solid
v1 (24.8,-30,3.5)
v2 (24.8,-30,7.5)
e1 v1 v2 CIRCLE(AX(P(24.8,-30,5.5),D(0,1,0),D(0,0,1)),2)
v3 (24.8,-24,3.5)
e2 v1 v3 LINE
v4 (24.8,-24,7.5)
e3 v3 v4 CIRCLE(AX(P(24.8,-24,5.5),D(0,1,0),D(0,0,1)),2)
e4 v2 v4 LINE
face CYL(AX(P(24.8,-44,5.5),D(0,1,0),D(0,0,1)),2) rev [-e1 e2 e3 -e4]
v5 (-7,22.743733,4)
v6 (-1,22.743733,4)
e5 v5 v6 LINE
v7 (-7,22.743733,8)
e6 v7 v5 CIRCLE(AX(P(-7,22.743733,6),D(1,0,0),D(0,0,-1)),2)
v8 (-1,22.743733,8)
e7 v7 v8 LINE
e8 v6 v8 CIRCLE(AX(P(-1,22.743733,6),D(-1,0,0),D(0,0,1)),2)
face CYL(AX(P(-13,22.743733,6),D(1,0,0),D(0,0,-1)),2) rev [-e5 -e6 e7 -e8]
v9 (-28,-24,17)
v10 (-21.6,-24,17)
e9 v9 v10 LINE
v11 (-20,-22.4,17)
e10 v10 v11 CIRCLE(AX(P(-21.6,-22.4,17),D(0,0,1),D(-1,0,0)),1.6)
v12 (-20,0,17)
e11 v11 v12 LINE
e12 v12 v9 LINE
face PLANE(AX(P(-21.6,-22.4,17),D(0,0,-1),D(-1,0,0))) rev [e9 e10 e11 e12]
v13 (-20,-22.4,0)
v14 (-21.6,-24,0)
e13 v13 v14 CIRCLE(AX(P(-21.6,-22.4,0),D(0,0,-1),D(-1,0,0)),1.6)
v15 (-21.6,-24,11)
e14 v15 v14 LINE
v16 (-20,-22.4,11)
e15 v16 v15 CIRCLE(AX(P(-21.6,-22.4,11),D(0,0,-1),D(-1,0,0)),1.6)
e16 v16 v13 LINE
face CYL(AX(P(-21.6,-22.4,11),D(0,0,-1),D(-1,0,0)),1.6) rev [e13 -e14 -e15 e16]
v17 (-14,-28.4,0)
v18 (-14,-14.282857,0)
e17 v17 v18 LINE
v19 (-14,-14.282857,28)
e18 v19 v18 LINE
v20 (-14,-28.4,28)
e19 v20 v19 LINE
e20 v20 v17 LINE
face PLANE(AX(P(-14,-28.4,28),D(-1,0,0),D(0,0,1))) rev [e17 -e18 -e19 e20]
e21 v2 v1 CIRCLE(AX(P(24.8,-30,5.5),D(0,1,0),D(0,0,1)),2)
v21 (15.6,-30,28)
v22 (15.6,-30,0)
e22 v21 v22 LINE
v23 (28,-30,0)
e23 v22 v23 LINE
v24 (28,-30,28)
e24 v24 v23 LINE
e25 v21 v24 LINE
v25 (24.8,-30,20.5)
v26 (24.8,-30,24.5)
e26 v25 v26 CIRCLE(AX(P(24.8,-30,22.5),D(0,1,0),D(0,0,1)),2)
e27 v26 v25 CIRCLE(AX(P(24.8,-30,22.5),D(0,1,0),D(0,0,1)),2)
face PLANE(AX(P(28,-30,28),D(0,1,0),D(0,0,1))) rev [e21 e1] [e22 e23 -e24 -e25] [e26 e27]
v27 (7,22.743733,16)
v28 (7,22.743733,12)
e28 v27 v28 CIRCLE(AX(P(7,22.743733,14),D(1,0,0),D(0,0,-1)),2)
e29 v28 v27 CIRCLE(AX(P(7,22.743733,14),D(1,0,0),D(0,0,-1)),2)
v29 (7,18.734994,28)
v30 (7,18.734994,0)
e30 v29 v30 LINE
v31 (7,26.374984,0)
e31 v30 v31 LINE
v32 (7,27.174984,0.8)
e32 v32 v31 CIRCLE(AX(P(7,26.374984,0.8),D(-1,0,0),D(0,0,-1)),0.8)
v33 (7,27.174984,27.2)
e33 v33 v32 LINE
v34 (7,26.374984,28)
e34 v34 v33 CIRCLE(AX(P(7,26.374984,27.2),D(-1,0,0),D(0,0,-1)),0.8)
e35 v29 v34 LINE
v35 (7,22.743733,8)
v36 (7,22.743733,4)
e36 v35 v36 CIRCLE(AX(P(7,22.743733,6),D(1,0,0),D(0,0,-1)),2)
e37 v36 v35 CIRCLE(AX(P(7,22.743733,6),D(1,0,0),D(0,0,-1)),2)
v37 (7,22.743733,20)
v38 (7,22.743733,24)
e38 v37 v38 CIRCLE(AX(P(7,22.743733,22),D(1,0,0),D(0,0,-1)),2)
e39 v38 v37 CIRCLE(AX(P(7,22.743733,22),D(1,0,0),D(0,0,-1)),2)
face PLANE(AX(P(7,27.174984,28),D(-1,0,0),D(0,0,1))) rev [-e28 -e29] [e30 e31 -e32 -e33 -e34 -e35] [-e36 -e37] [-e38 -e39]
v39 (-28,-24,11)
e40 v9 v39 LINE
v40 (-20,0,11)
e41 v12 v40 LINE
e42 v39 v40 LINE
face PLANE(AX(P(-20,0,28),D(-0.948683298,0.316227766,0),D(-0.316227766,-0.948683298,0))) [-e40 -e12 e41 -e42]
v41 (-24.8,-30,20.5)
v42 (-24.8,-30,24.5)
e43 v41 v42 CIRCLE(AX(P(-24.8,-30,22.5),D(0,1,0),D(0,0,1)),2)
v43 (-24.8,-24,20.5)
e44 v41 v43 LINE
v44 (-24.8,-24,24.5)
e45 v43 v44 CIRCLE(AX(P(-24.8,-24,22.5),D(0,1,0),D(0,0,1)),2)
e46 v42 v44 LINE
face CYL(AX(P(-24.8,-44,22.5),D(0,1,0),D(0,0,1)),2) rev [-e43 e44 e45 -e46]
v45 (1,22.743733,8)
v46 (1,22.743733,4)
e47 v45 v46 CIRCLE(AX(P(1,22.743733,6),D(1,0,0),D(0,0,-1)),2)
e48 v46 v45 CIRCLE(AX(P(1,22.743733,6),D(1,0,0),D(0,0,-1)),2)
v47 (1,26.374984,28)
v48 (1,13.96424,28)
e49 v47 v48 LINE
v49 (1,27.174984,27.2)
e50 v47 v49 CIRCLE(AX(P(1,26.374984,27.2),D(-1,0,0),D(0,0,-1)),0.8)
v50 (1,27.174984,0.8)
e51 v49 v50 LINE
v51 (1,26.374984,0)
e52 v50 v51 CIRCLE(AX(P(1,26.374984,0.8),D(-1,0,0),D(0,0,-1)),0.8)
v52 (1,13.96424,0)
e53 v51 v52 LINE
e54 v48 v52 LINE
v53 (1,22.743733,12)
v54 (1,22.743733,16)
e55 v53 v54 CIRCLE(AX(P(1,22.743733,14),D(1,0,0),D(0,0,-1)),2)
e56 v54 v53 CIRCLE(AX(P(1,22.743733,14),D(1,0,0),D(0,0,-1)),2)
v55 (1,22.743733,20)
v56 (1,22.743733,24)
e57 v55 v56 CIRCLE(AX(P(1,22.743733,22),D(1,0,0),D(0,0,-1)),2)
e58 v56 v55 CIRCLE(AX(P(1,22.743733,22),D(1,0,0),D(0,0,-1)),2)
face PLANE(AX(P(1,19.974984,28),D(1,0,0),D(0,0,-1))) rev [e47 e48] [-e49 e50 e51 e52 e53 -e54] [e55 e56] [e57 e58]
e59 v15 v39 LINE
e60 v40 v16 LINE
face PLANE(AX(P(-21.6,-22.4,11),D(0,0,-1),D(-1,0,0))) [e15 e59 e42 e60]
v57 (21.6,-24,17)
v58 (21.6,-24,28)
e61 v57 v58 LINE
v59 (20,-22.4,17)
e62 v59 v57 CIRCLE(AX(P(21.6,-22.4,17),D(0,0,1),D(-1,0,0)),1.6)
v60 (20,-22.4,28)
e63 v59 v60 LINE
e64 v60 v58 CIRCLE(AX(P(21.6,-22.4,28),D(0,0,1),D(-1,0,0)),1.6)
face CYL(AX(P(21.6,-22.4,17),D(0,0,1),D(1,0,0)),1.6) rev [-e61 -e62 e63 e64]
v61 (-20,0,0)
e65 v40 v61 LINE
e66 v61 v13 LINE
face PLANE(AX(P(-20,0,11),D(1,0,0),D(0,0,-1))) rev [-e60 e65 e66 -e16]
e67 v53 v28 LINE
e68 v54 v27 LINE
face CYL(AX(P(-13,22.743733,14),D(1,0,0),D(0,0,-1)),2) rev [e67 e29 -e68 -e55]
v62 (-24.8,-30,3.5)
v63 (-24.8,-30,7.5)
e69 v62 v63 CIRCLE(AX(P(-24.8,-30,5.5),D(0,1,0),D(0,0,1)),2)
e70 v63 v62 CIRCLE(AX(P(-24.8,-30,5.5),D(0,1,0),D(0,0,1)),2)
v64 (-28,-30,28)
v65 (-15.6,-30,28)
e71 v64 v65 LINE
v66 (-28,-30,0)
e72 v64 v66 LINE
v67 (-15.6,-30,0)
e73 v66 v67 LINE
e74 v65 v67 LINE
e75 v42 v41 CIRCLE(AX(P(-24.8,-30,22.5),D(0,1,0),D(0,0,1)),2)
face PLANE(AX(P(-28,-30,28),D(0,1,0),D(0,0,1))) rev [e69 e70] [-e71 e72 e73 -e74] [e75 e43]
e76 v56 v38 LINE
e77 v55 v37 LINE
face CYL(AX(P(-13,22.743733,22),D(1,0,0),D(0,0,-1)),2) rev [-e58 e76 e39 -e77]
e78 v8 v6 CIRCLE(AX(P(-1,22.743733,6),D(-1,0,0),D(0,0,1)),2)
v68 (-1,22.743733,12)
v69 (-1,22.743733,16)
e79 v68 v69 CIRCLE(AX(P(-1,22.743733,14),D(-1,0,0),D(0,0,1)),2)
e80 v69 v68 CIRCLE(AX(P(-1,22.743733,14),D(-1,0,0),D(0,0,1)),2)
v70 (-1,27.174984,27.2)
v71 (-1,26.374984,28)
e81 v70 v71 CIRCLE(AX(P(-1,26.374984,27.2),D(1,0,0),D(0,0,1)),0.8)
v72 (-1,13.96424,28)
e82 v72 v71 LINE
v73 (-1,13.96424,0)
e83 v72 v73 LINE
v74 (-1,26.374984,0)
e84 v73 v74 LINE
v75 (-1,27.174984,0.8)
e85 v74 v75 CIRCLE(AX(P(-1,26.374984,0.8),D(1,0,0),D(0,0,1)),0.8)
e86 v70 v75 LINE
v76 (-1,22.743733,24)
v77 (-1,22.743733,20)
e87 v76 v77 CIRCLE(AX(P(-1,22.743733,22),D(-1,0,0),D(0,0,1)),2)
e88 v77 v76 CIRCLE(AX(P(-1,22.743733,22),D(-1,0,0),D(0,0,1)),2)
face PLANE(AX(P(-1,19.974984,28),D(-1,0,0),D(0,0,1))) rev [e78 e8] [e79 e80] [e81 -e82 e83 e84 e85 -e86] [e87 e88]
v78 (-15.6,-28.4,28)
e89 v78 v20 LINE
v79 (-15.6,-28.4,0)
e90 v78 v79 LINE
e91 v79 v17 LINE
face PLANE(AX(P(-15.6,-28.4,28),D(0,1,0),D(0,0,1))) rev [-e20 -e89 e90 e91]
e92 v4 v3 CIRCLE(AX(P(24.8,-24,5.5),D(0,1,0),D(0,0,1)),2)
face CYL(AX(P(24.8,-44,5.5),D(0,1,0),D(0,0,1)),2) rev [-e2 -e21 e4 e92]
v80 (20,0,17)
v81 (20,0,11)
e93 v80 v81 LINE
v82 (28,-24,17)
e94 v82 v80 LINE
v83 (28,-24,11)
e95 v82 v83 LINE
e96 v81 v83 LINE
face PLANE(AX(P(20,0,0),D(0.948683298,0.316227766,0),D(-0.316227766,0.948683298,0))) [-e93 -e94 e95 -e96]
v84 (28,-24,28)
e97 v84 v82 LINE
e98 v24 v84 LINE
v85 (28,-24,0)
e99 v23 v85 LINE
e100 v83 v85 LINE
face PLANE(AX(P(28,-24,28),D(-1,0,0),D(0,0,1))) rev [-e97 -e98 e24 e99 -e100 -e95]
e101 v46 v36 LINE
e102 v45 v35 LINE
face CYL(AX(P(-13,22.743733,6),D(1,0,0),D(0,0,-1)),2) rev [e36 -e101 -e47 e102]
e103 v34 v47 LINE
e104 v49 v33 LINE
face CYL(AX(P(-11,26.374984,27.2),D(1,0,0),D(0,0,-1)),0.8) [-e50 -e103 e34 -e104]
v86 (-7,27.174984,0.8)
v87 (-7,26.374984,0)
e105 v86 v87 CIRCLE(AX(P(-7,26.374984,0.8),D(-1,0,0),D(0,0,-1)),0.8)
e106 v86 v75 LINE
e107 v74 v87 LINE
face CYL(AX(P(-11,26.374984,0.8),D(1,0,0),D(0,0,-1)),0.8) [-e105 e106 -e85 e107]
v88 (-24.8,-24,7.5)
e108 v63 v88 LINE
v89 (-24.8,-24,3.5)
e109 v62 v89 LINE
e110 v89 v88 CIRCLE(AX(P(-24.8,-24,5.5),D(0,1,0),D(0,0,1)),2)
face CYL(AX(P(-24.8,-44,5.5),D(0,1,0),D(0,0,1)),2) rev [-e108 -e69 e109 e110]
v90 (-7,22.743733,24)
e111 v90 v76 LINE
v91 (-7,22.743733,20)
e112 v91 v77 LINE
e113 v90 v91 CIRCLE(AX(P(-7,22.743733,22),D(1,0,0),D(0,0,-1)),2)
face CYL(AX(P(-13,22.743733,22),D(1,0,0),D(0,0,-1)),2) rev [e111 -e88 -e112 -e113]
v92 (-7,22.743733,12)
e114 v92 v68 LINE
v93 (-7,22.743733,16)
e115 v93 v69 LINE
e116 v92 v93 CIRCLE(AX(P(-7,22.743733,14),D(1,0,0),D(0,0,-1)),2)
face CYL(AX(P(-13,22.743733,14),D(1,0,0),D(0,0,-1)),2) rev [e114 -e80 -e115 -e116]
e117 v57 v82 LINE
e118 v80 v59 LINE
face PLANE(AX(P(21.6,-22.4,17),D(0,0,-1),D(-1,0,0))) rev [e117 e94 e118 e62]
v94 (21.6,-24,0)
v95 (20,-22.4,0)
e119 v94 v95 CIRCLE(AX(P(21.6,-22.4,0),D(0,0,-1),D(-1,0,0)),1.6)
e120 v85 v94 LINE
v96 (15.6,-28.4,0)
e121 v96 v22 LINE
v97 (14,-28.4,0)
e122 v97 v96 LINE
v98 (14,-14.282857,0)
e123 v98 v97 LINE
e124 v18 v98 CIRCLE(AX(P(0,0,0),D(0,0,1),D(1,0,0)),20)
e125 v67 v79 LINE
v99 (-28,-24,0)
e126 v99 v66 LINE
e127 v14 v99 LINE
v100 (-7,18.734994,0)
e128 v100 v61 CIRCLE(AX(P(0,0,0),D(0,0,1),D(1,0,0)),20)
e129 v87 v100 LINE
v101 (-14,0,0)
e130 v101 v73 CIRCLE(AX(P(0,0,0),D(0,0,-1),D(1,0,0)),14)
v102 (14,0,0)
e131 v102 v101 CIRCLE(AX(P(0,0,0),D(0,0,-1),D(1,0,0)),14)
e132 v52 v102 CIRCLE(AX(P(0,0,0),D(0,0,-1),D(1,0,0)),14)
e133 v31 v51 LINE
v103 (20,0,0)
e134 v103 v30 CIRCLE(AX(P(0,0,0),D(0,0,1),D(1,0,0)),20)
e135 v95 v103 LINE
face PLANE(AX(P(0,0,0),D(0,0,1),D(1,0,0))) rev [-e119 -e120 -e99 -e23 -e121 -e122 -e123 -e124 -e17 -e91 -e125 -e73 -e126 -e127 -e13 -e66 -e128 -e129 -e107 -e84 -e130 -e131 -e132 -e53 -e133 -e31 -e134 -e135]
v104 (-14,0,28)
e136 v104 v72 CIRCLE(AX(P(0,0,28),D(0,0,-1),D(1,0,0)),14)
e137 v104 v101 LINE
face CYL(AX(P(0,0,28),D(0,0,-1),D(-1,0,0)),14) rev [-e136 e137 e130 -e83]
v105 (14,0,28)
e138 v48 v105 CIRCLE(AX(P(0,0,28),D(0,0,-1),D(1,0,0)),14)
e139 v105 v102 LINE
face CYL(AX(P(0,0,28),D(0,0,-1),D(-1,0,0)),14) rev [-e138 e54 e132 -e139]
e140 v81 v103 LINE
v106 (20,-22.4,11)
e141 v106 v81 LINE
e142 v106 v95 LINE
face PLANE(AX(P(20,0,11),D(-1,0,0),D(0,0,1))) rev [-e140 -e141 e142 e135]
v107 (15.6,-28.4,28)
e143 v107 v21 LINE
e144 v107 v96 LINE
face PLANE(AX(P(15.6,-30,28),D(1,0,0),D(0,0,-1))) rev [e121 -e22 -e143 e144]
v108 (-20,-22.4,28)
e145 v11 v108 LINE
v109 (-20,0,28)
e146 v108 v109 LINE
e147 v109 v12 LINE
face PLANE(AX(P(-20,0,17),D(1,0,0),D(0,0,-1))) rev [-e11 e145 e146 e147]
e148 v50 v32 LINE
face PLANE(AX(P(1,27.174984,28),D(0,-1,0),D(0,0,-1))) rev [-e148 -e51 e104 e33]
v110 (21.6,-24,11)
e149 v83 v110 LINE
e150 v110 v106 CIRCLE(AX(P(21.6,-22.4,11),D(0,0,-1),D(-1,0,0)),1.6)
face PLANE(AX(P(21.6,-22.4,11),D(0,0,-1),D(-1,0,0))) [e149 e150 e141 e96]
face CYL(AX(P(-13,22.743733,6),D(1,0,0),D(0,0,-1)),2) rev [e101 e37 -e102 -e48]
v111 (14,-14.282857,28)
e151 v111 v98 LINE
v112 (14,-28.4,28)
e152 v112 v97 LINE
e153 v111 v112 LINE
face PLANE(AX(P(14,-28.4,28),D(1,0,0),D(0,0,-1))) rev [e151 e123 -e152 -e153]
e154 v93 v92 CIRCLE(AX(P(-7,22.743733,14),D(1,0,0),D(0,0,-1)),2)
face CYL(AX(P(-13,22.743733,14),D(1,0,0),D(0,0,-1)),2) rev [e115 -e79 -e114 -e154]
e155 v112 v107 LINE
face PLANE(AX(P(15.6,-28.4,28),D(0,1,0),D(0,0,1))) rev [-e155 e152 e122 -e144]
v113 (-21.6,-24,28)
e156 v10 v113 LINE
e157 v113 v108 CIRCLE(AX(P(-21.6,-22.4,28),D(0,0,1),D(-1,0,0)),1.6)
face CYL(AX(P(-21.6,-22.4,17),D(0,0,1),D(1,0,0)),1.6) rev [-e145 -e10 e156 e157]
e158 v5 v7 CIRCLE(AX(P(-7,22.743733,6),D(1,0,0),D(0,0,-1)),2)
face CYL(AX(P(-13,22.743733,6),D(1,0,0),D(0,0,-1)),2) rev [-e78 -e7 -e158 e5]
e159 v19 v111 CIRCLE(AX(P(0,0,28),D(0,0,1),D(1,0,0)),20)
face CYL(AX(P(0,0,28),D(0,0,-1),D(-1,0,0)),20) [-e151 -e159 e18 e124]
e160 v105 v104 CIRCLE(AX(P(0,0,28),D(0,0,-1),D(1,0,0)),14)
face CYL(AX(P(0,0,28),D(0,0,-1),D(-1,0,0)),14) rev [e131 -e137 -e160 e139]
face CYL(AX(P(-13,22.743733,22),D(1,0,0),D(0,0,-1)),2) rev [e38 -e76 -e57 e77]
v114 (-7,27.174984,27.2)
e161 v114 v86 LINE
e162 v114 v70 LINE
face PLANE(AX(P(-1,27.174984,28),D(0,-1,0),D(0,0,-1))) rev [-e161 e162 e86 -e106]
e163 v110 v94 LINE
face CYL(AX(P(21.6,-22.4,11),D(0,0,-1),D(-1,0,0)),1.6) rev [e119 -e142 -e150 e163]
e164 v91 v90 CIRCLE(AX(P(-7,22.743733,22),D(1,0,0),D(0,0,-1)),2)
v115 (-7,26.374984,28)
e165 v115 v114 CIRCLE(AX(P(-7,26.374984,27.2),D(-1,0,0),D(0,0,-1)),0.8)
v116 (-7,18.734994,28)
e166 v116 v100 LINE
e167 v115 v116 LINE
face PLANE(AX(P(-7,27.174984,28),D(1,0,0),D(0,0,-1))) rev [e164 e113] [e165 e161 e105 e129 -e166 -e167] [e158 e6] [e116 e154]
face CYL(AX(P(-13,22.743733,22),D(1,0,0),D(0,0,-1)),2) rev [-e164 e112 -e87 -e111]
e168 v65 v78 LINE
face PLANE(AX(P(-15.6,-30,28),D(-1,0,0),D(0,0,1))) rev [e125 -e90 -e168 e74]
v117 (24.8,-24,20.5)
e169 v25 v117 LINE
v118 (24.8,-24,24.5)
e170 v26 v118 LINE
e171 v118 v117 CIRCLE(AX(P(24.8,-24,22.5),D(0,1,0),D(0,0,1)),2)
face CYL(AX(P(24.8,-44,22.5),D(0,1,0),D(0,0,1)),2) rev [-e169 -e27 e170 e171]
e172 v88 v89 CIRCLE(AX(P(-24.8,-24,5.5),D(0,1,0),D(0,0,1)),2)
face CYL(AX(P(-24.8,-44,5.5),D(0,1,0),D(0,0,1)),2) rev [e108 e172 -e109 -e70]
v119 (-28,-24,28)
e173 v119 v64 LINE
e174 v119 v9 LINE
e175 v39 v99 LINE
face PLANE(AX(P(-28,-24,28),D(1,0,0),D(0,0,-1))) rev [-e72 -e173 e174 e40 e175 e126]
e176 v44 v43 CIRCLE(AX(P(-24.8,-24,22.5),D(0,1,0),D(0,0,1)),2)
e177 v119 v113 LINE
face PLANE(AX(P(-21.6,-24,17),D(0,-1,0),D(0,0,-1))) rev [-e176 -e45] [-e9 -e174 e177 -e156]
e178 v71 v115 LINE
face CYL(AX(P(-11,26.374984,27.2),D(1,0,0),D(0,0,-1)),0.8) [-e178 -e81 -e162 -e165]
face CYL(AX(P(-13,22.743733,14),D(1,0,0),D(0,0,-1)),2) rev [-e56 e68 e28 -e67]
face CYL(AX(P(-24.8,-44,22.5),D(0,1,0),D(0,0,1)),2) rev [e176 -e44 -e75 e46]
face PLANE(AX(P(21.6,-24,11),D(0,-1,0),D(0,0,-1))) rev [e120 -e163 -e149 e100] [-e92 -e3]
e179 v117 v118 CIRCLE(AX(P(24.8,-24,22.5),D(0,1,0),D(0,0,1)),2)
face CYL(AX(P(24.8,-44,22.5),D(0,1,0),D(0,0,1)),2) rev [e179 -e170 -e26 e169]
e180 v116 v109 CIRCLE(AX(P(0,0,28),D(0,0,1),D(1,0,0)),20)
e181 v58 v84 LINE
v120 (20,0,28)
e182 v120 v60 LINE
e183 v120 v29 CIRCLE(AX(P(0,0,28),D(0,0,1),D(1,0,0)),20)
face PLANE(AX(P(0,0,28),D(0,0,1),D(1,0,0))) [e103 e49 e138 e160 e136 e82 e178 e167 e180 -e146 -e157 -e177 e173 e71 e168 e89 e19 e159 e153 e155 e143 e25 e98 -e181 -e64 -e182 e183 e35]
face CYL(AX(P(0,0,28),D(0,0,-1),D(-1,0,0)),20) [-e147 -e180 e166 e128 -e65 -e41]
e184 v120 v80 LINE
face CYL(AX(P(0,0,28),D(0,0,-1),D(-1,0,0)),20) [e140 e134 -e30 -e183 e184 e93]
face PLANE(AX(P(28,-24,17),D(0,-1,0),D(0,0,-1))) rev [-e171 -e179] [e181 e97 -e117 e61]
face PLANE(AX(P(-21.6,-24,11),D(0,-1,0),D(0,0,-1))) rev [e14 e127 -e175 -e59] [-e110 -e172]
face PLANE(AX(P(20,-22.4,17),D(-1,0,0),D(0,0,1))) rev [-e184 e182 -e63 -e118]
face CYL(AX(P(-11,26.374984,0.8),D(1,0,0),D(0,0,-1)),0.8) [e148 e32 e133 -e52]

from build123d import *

# Parameters (mm, degrees)
CLAMP_BODY_DEPTH             = 28
SIDE_RECESS_A_DEPTH          = 18
SIDE_RECESS_B_DEPTH          = 18
LOWER_START                  = -28
LOWER_SIDE_BOSS_DEPTH        = 28
LOWER_BOSS_RELIEF_A_DEPTH    = 11
LOWER_START_2                = -11
LOWER_BOSS_RELIEF_B_DEPTH    = 11
UPPER_SIDE_BOSS_DEPTH        = 28
UPPER_BOSS_RELIEF_A_DEPTH    = 11
UPPER_START                  = -11
UPPER_BOSS_RELIEF_B_DEPTH    = 11
CLAMP_SCREW_HOLES_SKETCH_R   = 2
CLAMP_SCREW_HOLES_3X_DEPTH   = 20
FOOT_MOUNTING_HOLES_SKETCH_R = 2
FOOT_MOUNTING_HOLES_DEPTH    = 20


with BuildPart() as part:
    # Clamp Body Profile → Clamp Body (new body)
    with BuildSketch(Plane.XY):
        with BuildLine():
            Line((-20, 0), (-20, -22.4))
            ThreePointArc((-20, -22.4), (-20.46862915, -23.53137085), (-21.6, -24))
            Line((-21.6, -24), (-28, -24))
            Line((-28, -24), (-28, -30))
            Line((-28, -30), (-15.6, -30))
            Line((-15.6, -30), (-15.6, -28.4))
            Line((-15.6, -28.4), (-14, -28.4))
            Line((-14, -28.4), (-14, -14.282856857))
            ThreePointArc((-14, -14.282856857), (0, -20), (14, -14.282856857))
            Line((14, -14.282856857), (14, -28.4))
            Line((14, -28.4), (15.6, -28.4))
            Line((15.6, -28.4), (15.6, -30))
            Line((15.6, -30), (28, -30))
            Line((28, -30), (28, -24))
            Line((28, -24), (21.6, -24))
            ThreePointArc((21.6, -24), (20.46862915, -23.53137085), (20, -22.4))
            Line((20, -22.4), (20, 0))
            ThreePointArc((20, 0), (16.431676725, 11.401754251), (7, 18.734993995))
            Line((7, 18.734993995), (7, 27.174984355))
            Line((7, 27.174984355), (1, 27.174984355))
            Line((1, 27.174984355), (1, 19.974984355))
            Line((1, 19.974984355), (1, 13.964240044))
            ThreePointArc((1, 13.964240044), (0, -14), (-1, 13.964240044))
            Line((-1, 13.964240044), (-1, 19.974984355))
            Line((-1, 19.974984355), (-1, 27.174984355))
            Line((-1, 27.174984355), (-7, 27.174984355))
            Line((-7, 27.174984355), (-7, 18.734993995))
            ThreePointArc((-7, 18.734993995), (-16.431676725, 11.401754251), (-20, 0))
        make_face()
    extrude(amount=CLAMP_BODY_DEPTH)

    # Side Recess A Sketch → Side Recess A (cut)
    with BuildSketch(Plane(origin=(7, 0, 0), x_dir=(0, 0, -1), z_dir=(1, 0, 0))):
        with BuildLine():
            Line((-28, 26.374984355), (-28, 27.174984355))
            Line((-28, 27.174984355), (-27.2, 27.174984355))
            ThreePointArc((-27.2, 27.174984355), (-27.765685425, 26.94066978), (-28, 26.374984355))
        make_face()
    extrude(amount=-SIDE_RECESS_A_DEPTH, mode=Mode.SUBTRACT)

    # Side Recess B Sketch → Side Recess B (cut)
    with BuildSketch(Plane(origin=(7, 0, 0), x_dir=(0, 0, -1), z_dir=(1, 0, 0))):
        with BuildLine():
            Line((0, 27.174984355), (0, 26.374984355))
            ThreePointArc((0, 26.374984355), (-0.234314575, 26.94066978), (-0.8, 27.174984355))
            Line((-0.8, 27.174984355), (0, 27.174984355))
        make_face()
    extrude(amount=-SIDE_RECESS_B_DEPTH, mode=Mode.SUBTRACT)

    # Lower Side Boss Sketch → Lower Side Boss (add)
    with BuildSketch(Plane.XY.offset(28).offset(LOWER_START)):
        with BuildLine():
            Line((20, 0), (28, -24))
            Line((28, -24), (21.6, -24))
            ThreePointArc((21.6, -24), (20.46862915, -23.53137085), (20, -22.4))
            Line((20, -22.4), (20, 0))
        make_face()
    extrude(amount=LOWER_SIDE_BOSS_DEPTH)

    # Lower Boss Relief A Sketch → Lower Boss Relief A (cut)
    with BuildSketch(Plane.XY.offset(28)):
        with BuildLine():
            Line((20, 0), (28, -24))
            Line((28, -24), (21.6, -24))
            ThreePointArc((21.6, -24), (20.46862915, -23.53137085), (20, -22.4))
            Line((20, -22.4), (20, 0))
        make_face()
    extrude(amount=-LOWER_BOSS_RELIEF_A_DEPTH, mode=Mode.SUBTRACT)

    # Lower Boss Relief B Sketch → Lower Boss Relief B (cut)
    with BuildSketch(Plane(origin=(0, 0, 0), x_dir=(-1, 0, 0), z_dir=(0, 0, -1)).offset(LOWER_START_2)):
        with BuildLine():
            Line((-20, 0), (-20, -22.4))
            ThreePointArc((-20, -22.4), (-20.46862915, -23.53137085), (-21.6, -24))
            Line((-21.6, -24), (-28, -24))
            Line((-28, -24), (-20, 0))
        make_face()
    extrude(amount=LOWER_BOSS_RELIEF_B_DEPTH, mode=Mode.SUBTRACT)

    # Upper Side Boss Sketch → Upper Side Boss (add)
    with BuildSketch(Plane(origin=(0, 0, 0), x_dir=(-1, 0, 0), z_dir=(0, 0, -1))):
        with BuildLine():
            Line((20, 0), (28, -24))
            Line((28, -24), (21.6, -24))
            ThreePointArc((21.6, -24), (20.46862915, -23.53137085), (20, -22.4))
            Line((20, -22.4), (20, 0))
        make_face()
    extrude(amount=-UPPER_SIDE_BOSS_DEPTH)

    # Upper Boss Relief A Sketch → Upper Boss Relief A (cut)
    with BuildSketch(Plane(origin=(0, 0, 0), x_dir=(-1, 0, 0), z_dir=(0, 0, -1))):
        with BuildLine():
            Line((20, 0), (20, -22.4))
            ThreePointArc((20, -22.4), (20.46862915, -23.53137085), (21.6, -24))
            Line((21.6, -24), (28, -24))
            Line((28, -24), (20, 0))
        make_face()
    extrude(amount=-UPPER_BOSS_RELIEF_A_DEPTH, mode=Mode.SUBTRACT)

    # Upper Boss Relief B Sketch → Upper Boss Relief B (cut)
    with BuildSketch(Plane.XY.offset(28).offset(UPPER_START)):
        with BuildLine():
            Line((-20, 0), (-20, -22.4))
            ThreePointArc((-20, -22.4), (-20.46862915, -23.53137085), (-21.6, -24))
            Line((-21.6, -24), (-28, -24))
            Line((-28, -24), (-20, 0))
        make_face()
    extrude(amount=UPPER_BOSS_RELIEF_B_DEPTH, mode=Mode.SUBTRACT)

    # Clamp Screw Holes Sketch → Clamp Screw Holes 3x (cut)
    with BuildSketch(Plane(origin=(7, 0, 0), x_dir=(0, 0, -1), z_dir=(1, 0, 0))):
        with Locations((-22, 22.743733378)):
            Circle(CLAMP_SCREW_HOLES_SKETCH_R)
        with Locations((-14, 22.743733378)):
            Circle(CLAMP_SCREW_HOLES_SKETCH_R)
        with Locations((-6, 22.743733378)):
            Circle(CLAMP_SCREW_HOLES_SKETCH_R)
    extrude(amount=-CLAMP_SCREW_HOLES_3X_DEPTH, mode=Mode.SUBTRACT)

    # Foot Mounting Holes Sketch → Foot Mounting Holes (cut)
    with BuildSketch(Plane(origin=(0, -24, 0), x_dir=(1, 0, 0), z_dir=(0, 1, 0))):
        with Locations(Location((24.8, -22.5, 0), (0, 0, 270))):
            Circle(FOOT_MOUNTING_HOLES_SKETCH_R)
        with Locations(Location((24.8, -5.5, 0), (0, 0, 270))):
            Circle(FOOT_MOUNTING_HOLES_SKETCH_R)
        with Locations(Location((-24.8, -5.5, 0), (0, 0, 270))):
            Circle(FOOT_MOUNTING_HOLES_SKETCH_R)
        with Locations(Location((-24.8, -22.5, 0), (0, 0, 270))):
            Circle(FOOT_MOUNTING_HOLES_SKETCH_R)
    extrude(amount=-FOOT_MOUNTING_HOLES_DEPTH, mode=Mode.SUBTRACT)


solid = part.part
